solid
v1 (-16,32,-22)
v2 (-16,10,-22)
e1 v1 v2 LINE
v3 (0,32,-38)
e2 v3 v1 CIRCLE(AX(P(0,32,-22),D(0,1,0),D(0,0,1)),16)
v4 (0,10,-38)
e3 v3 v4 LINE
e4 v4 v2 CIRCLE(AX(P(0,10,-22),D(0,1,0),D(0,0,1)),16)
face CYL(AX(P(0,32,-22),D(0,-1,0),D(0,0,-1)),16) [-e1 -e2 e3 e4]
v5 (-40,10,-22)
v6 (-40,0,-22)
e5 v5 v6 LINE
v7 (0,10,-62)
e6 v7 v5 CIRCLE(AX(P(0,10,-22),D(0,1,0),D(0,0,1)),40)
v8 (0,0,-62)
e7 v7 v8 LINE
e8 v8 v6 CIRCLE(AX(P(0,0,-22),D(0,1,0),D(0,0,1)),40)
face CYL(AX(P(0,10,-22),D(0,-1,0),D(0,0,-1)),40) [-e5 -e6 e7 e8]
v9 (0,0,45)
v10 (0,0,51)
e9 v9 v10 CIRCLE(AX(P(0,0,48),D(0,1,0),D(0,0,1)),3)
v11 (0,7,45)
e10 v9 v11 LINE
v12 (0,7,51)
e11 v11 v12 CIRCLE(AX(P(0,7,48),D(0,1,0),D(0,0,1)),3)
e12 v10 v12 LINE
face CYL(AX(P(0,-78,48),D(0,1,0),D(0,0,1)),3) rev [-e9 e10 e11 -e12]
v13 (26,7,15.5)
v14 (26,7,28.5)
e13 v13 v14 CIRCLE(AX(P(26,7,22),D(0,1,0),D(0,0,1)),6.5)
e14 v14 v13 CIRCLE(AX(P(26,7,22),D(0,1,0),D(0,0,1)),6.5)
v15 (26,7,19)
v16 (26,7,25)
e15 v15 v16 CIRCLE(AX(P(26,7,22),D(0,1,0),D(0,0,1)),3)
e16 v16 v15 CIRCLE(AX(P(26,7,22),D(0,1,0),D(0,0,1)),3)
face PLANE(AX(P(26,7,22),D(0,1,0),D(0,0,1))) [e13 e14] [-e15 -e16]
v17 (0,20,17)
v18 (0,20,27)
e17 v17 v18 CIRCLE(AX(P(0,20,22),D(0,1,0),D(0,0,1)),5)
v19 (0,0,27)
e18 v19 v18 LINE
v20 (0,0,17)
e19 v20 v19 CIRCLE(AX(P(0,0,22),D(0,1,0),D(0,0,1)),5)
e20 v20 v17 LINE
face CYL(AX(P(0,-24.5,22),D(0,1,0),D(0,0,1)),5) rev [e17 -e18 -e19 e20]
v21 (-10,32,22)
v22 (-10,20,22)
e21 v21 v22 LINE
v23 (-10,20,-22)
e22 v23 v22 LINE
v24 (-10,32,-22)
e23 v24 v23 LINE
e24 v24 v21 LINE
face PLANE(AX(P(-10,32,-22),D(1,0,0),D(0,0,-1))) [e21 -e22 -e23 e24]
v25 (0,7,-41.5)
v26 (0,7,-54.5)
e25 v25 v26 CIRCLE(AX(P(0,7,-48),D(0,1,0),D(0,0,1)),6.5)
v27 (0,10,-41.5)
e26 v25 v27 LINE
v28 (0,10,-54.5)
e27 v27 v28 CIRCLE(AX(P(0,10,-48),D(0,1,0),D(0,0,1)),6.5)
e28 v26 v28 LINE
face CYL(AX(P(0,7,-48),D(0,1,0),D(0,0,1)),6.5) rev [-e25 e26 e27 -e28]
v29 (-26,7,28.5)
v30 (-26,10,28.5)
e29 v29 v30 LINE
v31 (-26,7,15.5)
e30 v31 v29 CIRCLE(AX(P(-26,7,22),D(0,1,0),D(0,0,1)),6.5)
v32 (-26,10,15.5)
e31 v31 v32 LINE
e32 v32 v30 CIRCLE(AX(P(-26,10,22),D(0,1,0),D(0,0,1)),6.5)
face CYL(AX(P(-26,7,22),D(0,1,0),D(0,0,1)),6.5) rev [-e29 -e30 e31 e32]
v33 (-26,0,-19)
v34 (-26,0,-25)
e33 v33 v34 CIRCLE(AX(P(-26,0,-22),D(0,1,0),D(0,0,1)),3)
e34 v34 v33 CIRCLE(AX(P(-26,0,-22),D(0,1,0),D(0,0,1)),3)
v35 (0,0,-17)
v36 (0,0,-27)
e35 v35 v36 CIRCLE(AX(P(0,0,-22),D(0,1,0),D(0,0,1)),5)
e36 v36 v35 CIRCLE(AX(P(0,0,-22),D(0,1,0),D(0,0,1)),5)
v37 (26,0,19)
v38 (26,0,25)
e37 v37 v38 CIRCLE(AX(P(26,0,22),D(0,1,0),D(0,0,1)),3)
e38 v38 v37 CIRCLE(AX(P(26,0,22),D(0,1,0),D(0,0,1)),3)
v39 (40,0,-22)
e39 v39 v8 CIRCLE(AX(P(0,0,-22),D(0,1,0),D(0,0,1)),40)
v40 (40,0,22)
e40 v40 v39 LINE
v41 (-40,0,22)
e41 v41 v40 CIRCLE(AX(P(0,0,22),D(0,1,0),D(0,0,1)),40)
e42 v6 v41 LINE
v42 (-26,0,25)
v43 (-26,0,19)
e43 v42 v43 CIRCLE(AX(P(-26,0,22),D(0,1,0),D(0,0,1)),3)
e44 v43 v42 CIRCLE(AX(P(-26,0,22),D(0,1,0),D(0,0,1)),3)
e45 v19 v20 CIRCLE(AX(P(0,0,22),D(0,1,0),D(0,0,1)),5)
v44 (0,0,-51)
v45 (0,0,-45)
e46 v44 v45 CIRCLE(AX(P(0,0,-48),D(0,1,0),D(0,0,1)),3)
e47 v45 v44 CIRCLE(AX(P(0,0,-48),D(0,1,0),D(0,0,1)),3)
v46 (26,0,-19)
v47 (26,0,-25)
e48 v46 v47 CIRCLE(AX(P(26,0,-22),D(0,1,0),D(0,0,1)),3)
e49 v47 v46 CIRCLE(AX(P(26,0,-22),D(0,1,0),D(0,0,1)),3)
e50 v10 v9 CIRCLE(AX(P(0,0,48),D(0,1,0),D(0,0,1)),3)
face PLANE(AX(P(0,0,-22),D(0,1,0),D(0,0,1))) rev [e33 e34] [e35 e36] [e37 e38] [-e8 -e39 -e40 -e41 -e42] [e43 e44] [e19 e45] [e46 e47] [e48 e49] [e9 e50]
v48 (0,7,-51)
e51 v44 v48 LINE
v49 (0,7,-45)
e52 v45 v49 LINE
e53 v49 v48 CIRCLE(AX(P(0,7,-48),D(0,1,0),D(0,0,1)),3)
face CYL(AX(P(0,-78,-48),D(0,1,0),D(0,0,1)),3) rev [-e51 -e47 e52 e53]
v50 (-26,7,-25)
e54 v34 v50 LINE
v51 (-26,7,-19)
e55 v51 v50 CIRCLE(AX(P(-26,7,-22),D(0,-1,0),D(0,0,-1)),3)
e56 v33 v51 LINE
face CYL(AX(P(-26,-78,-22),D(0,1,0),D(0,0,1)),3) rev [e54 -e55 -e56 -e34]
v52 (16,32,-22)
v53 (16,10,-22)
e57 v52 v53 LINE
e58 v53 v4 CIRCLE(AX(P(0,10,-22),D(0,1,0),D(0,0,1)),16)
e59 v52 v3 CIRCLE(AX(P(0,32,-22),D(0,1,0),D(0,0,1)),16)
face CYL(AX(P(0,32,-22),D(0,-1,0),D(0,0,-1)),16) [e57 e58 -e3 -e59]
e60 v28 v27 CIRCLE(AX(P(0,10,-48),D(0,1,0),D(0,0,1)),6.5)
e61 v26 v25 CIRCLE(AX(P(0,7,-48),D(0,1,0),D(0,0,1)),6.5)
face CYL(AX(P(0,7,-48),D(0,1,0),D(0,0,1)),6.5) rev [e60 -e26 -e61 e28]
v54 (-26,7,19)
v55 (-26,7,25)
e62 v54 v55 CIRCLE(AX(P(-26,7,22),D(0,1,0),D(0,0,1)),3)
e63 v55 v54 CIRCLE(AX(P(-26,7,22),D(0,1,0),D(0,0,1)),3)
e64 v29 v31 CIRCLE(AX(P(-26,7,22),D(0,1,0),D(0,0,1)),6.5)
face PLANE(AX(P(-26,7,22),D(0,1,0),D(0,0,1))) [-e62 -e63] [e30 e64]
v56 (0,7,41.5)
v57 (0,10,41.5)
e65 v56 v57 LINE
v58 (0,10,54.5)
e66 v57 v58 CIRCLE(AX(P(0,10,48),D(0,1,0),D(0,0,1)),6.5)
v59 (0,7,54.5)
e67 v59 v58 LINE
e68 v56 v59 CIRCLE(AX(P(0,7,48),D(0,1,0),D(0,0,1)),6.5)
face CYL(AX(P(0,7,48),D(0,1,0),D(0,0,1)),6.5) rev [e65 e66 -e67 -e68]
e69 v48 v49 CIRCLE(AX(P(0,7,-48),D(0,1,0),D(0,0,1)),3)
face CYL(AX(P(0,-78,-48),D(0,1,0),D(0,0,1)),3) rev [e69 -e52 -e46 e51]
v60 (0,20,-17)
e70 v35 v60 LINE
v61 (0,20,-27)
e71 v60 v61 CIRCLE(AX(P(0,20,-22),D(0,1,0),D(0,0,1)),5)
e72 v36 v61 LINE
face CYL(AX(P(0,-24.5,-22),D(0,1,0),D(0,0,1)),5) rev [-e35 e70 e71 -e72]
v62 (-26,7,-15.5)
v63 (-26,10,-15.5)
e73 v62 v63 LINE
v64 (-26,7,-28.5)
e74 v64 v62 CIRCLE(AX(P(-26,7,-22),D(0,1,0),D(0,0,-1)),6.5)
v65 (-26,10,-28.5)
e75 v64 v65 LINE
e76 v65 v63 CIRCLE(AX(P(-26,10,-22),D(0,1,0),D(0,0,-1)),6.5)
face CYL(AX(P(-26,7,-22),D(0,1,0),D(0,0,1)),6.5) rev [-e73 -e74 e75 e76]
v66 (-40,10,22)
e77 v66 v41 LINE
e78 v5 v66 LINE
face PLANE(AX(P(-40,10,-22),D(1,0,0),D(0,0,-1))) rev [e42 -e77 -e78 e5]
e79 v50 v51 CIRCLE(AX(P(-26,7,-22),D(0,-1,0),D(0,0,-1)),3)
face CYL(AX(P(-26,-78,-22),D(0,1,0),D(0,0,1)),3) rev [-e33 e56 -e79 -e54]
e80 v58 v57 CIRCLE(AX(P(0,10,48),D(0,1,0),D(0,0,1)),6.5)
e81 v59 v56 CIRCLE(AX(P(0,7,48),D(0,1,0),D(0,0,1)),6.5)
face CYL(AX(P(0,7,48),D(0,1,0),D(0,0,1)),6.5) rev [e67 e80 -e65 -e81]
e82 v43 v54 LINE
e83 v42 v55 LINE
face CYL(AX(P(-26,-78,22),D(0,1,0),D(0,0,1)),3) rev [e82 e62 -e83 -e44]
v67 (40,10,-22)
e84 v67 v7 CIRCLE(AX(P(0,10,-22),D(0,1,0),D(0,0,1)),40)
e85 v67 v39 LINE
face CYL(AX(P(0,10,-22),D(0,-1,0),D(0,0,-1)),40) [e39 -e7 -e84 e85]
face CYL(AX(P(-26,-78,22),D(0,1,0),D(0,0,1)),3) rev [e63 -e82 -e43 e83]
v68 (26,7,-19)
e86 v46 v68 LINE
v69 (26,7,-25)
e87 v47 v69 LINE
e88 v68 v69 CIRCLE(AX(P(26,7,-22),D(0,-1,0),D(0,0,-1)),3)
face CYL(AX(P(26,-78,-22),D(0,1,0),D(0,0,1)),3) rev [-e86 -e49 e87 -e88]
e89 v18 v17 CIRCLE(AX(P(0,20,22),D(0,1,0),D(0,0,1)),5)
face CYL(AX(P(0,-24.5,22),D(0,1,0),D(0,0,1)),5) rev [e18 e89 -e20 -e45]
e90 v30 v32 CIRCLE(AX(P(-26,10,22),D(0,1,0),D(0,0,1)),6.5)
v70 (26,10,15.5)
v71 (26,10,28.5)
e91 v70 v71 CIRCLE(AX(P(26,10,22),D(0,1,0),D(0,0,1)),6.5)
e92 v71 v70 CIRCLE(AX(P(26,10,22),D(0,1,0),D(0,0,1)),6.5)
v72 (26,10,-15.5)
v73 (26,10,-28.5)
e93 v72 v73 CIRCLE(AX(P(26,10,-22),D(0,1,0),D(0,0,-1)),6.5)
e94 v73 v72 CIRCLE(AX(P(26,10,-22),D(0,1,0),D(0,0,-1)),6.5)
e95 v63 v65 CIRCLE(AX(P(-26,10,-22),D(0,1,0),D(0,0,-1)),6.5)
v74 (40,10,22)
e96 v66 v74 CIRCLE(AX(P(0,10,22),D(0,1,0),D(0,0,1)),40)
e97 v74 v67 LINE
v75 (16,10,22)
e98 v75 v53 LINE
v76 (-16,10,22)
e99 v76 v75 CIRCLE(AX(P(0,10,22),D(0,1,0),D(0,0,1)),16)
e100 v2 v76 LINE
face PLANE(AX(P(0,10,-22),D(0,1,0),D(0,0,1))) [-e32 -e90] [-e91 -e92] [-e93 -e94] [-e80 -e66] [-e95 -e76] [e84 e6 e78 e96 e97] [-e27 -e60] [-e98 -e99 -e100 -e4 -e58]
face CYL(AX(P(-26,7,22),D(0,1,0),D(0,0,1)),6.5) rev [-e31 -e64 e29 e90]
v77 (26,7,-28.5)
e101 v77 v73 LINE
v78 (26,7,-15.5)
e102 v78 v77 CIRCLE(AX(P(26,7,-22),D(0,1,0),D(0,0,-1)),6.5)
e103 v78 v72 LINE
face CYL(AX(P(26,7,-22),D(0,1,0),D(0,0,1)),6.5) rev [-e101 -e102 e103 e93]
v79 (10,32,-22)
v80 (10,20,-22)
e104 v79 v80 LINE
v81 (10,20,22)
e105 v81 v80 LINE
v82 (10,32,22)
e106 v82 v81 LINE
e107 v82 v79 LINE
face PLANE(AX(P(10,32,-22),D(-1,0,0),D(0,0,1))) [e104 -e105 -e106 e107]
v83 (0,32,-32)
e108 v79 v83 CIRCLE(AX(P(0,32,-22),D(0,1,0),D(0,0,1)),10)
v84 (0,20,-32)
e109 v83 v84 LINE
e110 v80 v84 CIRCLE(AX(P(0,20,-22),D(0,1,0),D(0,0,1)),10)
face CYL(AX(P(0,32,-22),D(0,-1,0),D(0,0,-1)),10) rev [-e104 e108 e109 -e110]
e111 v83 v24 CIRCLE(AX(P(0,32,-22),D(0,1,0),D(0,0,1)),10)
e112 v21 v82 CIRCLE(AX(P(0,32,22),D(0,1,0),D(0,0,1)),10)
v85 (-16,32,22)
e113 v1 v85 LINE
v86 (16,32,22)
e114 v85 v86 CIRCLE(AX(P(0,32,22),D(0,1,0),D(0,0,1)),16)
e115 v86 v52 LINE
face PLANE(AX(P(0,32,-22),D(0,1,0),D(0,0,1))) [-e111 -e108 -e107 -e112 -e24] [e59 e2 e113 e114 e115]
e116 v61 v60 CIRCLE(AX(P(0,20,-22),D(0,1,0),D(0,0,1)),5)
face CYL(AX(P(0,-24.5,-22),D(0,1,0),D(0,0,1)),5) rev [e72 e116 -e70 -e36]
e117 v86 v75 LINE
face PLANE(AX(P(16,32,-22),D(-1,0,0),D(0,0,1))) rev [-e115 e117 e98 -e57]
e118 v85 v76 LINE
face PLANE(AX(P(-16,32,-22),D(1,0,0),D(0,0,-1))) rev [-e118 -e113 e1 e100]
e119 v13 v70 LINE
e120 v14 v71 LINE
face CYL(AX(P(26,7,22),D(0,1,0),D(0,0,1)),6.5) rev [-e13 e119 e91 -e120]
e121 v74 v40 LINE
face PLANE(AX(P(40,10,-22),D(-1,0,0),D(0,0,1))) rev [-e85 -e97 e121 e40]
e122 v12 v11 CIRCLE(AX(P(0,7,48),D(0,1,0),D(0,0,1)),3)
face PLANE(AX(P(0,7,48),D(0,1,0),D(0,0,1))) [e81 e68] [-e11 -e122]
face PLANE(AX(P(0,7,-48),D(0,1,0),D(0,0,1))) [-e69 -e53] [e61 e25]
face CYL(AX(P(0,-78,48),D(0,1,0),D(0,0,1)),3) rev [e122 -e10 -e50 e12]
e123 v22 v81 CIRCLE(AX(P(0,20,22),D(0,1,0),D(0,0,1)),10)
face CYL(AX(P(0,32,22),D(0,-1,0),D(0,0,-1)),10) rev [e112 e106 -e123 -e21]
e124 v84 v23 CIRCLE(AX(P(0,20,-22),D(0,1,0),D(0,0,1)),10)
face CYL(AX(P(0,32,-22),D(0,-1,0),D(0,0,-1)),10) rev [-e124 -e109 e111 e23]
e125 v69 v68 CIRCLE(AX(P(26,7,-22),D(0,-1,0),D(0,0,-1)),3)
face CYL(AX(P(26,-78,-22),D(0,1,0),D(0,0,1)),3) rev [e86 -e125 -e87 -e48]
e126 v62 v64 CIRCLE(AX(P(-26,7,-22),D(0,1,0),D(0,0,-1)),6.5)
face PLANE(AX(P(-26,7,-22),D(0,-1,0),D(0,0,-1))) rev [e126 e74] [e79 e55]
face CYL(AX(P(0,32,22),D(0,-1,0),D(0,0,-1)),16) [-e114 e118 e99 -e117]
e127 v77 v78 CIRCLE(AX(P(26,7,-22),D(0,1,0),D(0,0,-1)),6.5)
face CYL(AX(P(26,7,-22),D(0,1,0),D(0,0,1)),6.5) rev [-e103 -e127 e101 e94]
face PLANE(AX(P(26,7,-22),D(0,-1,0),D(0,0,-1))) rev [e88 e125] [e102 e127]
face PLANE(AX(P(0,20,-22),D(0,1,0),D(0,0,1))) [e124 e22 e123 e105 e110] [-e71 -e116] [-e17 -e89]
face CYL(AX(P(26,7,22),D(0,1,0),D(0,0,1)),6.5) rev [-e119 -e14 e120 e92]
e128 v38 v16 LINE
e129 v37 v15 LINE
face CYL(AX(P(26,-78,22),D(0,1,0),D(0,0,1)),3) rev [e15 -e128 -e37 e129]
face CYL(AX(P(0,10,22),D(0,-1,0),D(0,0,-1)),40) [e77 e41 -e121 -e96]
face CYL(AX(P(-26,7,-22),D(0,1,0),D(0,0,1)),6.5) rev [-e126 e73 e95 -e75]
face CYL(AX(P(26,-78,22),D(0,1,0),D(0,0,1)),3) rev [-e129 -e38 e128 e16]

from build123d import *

# Parameters (mm, degrees)
BASE_PLATE_DEPTH        = 10
SLOT_BOSS_DEPTH         = 22
SECONDARY_BOSS_DEPTH    = 10
SLOT_CUT_SKETCH_R       = 5
SLOT_THROUGH_CUT_DEPTH  = 34.5
COUNTERBORE_SKETCH_R    = 6.5
COUNTERBORES_6X_DEPTH   = 3
MOUNTING_HOLE_SKETCH_R  = 3
MOUNTING_HOLES_6X_DEPTH = 88


with BuildPart() as part:
    # Base Plate Sketch → Base Plate (new body)
    with BuildSketch(Plane(origin=(0, 0, 0), x_dir=(1, 0, 0), z_dir=(0, 1, 0))):
        with BuildLine():
            Line((40, 22), (40, -22))
            ThreePointArc((40, -22), (0, -62), (-40, -22))
            Line((-40, -22), (-40, 22))
            ThreePointArc((-40, 22), (0, 62), (40, 22))
        make_face()
    extrude(amount=BASE_PLATE_DEPTH)

    # Slot Boss Sketch → Slot Boss (add)
    with BuildSketch(Plane(origin=(0, 10, 0), x_dir=(1, 0, 0), z_dir=(0, 1, 0))):
        with BuildLine():
            Line((16, 22), (16, -22))
            ThreePointArc((16, -22), (0, -38), (-16, -22))
            Line((-16, -22), (-16, 22))
            ThreePointArc((-16, 22), (0, 38), (16, 22))
        make_face()
        with BuildLine():
            Line((10, 22), (10, -22))
            ThreePointArc((10, -22), (0, -32), (-10, -22))
            Line((-10, -22), (-10, 22))
            ThreePointArc((-10, 22), (0, 32), (10, 22))
        make_face(mode=Mode.SUBTRACT)
    extrude(amount=SLOT_BOSS_DEPTH)

    # Secondary Boss Sketch → Secondary Boss (add)
    with BuildSketch(Plane(origin=(0, 10, 0), x_dir=(1, 0, 0), z_dir=(0, 1, 0))):
        with BuildLine():
            Line((-10, 22), (-10, -22))
            ThreePointArc((-10, -22), (0, -32), (10, -22))
            Line((10, -22), (10, 22))
            ThreePointArc((10, 22), (0, 32), (-10, 22))
        make_face()
    extrude(amount=SECONDARY_BOSS_DEPTH)

    # Slot Cut Sketch → Slot Through Cut (cut, symmetric)
    with BuildSketch(Plane(origin=(0, 10, 0), x_dir=(1, 0, 0), z_dir=(0, 1, 0))):
        with Locations(Location((0, 22, 0), (0, 0, 270))):
            Circle(SLOT_CUT_SKETCH_R)
        with Locations(Location((0, -22, 0), (0, 0, 270))):
            Circle(SLOT_CUT_SKETCH_R)
    extrude(amount=SLOT_THROUGH_CUT_DEPTH, both=True, mode=Mode.SUBTRACT)

    # Counterbore Sketch → Counterbores 6x (cut)
    with BuildSketch(Plane(origin=(0, 10, 0), x_dir=(1, 0, 0), z_dir=(0, 1, 0))):
        with Locations(Location((0, -48, 0), (0, 0, 270))):
            Circle(COUNTERBORE_SKETCH_R)
        with Locations(Location((0, 48, 0), (0, 0, 270))):
            Circle(COUNTERBORE_SKETCH_R)
        with Locations(Location((26, -22, 0), (0, 0, 270))):
            Circle(COUNTERBORE_SKETCH_R)
        with Locations(Location((-26, -22, 0), (0, 0, 270))):
            Circle(COUNTERBORE_SKETCH_R)
        with Locations(Location((26, 22, 0), (0, 0, 90))):
            Circle(COUNTERBORE_SKETCH_R)
        with Locations(Location((-26, 22, 0), (0, 0, 90))):
            Circle(COUNTERBORE_SKETCH_R)
    extrude(amount=-COUNTERBORES_6X_DEPTH, mode=Mode.SUBTRACT)

    # Mounting Hole Sketch → Mounting Holes 6x (cut)
    with BuildSketch(Plane(origin=(0, 10, 0), x_dir=(1, 0, 0), z_dir=(0, 1, 0))):
        with Locations(Location((0, -48, 0), (0, 0, 270))):
            Circle(MOUNTING_HOLE_SKETCH_R)
        with Locations(Location((26, -22, 0), (0, 0, 270))):
            Circle(MOUNTING_HOLE_SKETCH_R)
        with Locations(Location((26, 22, 0), (0, 0, 270))):
            Circle(MOUNTING_HOLE_SKETCH_R)
        with Locations(Location((0, 48, 0), (0, 0, 270))):
            Circle(MOUNTING_HOLE_SKETCH_R)
        with Locations(Location((-26, 22, 0), (0, 0, 270))):
            Circle(MOUNTING_HOLE_SKETCH_R)
        with Locations(Location((-26, -22, 0), (0, 0, 270))):
            Circle(MOUNTING_HOLE_SKETCH_R)
    extrude(amount=-MOUNTING_HOLES_6X_DEPTH, mode=Mode.SUBTRACT)


solid = part.part
